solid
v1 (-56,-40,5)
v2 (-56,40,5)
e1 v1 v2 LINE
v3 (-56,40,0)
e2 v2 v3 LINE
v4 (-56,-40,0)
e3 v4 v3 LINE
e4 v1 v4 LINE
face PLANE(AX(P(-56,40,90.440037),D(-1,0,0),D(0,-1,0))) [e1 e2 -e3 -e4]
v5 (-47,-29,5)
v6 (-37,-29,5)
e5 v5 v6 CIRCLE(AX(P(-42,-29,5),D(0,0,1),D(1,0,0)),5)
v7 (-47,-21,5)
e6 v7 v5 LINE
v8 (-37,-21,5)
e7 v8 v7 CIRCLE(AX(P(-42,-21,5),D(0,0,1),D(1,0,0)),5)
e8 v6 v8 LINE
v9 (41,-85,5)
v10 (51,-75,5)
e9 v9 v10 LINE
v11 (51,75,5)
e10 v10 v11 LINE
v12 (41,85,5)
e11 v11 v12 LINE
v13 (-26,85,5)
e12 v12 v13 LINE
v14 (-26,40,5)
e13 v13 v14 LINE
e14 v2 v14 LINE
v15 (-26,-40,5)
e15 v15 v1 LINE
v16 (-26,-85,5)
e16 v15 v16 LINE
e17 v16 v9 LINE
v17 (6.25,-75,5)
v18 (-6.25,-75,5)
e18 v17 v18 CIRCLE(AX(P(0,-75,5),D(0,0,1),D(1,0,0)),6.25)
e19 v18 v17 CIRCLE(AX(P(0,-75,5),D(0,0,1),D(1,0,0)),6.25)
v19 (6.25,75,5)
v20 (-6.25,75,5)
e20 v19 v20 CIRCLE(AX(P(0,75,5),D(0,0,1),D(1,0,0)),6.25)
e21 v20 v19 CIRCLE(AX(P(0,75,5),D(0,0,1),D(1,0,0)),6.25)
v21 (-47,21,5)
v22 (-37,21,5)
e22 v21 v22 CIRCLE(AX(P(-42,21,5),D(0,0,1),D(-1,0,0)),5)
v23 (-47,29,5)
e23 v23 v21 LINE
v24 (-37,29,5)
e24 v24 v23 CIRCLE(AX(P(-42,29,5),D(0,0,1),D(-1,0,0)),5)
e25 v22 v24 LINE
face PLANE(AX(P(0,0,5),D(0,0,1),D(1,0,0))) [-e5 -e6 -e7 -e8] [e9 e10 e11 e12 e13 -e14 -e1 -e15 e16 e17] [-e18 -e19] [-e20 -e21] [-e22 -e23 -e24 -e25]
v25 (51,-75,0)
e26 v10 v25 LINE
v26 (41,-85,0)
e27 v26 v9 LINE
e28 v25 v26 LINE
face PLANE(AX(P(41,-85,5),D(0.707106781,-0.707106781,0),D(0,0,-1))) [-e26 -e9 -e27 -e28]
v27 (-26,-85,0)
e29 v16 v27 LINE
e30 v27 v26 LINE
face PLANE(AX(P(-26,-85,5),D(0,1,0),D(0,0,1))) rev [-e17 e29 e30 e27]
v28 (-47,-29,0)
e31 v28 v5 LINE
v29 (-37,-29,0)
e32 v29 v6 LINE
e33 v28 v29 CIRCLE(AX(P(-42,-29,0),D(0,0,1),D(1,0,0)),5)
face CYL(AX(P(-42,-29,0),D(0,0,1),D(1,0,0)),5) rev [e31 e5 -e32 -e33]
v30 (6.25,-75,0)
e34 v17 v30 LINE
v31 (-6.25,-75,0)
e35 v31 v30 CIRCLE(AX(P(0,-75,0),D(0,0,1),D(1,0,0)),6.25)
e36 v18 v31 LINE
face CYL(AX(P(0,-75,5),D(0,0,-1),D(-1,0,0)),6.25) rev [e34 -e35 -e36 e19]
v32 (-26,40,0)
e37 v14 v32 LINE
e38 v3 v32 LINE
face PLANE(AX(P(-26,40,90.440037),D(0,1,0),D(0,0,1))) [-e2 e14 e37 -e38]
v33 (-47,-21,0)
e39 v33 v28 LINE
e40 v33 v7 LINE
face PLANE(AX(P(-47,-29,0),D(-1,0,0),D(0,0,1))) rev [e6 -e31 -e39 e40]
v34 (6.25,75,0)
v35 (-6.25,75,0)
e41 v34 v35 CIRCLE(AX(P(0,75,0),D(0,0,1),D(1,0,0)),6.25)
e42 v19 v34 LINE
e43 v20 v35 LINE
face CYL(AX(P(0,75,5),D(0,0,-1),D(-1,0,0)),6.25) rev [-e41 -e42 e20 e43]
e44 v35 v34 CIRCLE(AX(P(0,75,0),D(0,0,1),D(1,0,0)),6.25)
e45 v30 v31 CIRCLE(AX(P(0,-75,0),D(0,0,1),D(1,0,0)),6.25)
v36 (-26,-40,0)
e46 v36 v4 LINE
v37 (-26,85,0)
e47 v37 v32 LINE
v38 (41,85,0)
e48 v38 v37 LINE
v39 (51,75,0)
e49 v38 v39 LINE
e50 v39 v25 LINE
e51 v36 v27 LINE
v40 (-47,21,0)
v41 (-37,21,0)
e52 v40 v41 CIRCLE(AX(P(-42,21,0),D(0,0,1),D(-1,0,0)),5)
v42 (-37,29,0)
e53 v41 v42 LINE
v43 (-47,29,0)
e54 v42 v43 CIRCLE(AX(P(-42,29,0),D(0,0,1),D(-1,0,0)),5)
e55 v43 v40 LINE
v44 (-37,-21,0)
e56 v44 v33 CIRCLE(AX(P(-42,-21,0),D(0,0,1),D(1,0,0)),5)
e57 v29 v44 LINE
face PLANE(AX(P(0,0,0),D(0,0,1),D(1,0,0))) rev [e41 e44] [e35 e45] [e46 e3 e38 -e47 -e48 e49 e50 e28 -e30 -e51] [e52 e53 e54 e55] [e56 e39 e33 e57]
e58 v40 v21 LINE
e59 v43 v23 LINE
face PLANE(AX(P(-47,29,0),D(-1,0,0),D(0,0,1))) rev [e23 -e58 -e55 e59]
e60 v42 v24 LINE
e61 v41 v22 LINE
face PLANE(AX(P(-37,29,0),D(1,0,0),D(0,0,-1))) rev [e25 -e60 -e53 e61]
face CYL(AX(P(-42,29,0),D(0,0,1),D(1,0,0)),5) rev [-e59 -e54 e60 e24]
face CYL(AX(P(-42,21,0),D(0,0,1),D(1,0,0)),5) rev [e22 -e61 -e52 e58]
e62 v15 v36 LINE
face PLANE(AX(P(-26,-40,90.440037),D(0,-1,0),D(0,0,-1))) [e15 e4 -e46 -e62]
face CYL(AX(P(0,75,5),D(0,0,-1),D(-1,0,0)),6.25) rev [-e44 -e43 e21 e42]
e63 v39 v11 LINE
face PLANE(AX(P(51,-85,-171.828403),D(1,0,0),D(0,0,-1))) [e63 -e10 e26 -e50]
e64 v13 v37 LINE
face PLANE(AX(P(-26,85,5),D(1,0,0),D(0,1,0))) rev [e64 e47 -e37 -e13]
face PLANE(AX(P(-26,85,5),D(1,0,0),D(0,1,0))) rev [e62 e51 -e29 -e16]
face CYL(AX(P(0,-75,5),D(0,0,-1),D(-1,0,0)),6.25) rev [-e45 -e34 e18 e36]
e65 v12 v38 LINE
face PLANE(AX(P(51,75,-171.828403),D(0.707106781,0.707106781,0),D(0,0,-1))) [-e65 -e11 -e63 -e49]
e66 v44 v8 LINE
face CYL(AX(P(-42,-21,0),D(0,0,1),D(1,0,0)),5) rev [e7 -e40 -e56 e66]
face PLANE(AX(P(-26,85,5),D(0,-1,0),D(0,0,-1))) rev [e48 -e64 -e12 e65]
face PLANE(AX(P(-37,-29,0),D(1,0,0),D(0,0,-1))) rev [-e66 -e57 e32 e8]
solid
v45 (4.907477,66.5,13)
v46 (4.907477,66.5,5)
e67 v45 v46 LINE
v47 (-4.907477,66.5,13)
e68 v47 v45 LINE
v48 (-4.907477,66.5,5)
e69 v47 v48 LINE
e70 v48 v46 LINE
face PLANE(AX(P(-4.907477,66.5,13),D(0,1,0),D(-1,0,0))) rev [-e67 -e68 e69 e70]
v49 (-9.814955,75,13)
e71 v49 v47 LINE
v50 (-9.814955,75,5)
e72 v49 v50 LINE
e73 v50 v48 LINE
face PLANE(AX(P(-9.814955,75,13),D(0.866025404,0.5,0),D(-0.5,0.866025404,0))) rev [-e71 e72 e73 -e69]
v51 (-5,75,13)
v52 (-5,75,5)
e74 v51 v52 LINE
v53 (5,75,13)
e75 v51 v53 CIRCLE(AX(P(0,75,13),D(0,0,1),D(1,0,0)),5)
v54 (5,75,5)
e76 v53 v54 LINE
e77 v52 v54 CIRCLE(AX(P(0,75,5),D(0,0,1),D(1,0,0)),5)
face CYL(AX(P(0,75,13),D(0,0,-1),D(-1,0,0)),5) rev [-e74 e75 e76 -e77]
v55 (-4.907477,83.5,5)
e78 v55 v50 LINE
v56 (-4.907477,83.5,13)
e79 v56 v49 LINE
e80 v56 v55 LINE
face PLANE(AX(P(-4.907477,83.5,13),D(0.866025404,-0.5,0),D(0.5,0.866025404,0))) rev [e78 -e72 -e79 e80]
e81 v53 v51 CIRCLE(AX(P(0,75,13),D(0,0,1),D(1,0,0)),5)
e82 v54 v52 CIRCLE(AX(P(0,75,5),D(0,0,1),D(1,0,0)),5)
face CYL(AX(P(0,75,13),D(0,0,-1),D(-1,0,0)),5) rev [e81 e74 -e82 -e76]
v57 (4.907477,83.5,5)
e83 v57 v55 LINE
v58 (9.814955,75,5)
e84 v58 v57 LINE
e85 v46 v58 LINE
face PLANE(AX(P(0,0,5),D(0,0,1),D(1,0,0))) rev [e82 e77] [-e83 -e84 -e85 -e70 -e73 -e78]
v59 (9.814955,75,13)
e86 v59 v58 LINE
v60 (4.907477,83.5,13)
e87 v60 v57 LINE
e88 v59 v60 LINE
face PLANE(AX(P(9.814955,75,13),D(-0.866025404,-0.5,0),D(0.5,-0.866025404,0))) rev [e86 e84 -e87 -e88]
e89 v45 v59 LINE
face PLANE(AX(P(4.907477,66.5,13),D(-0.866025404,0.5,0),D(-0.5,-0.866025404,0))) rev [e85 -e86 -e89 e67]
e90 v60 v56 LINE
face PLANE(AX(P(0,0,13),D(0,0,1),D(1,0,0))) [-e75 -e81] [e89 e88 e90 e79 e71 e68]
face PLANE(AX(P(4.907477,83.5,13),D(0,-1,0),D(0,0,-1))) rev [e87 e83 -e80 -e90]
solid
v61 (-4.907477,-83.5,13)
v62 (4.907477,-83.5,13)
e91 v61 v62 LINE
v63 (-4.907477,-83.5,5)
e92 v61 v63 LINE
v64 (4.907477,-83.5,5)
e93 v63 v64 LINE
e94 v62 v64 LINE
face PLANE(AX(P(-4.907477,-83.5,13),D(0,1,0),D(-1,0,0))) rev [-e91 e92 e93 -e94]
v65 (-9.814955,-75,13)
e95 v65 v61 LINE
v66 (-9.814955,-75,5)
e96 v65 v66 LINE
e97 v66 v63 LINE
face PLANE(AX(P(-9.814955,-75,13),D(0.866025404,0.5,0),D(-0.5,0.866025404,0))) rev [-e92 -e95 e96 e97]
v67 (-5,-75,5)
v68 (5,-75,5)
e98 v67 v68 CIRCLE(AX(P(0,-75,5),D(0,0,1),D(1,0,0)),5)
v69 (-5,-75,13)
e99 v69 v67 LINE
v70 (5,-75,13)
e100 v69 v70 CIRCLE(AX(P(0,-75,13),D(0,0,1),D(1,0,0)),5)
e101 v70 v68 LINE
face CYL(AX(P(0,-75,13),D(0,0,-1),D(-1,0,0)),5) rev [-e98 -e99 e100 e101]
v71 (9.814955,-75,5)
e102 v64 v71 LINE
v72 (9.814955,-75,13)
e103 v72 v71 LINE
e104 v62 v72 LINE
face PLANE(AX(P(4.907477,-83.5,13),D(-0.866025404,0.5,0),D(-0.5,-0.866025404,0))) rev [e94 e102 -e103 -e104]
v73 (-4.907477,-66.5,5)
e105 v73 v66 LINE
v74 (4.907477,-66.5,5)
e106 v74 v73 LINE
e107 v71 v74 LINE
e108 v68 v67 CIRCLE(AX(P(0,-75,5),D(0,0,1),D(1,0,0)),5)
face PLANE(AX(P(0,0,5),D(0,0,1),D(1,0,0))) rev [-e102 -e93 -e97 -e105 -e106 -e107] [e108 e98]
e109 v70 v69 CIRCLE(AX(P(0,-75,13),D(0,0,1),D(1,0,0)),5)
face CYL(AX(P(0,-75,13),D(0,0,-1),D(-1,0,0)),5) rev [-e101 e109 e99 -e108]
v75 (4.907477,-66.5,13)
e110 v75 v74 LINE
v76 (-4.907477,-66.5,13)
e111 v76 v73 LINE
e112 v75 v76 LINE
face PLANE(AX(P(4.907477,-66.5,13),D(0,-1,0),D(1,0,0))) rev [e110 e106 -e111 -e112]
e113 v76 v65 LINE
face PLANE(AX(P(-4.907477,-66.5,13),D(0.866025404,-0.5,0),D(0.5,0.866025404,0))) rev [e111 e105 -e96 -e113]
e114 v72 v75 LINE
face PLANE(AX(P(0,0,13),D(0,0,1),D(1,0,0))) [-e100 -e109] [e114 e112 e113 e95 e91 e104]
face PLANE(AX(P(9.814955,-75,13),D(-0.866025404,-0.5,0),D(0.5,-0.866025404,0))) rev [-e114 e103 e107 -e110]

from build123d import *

# Parameters (mm, degrees)
SKETCH_1_W            = 52
SKETCH_1_H            = 170
SKETCH_1_R            = 6.25
EXTRUDE_392_DEPTH     = 5
SKETCH_6_W            = 30
SKETCH_6_H            = 80
EXTRUDE_644_DEPTH     = 5
CUT_EXTRUDE_947_DEPTH = 102.911726509
SKETCH_3_R            = 5
EXTRUDE_2_DEPTH       = 8
EXTRUDE_2_2_DEPTH     = 8
SKETCH_11_W           = 25
SKETCH_11_H           = 170
EXTRUDE_3_DEPTH       = 5
CHAMFER_6_SIZE        = 10


with BuildPart() as part:
    # 草图1 → Extrude 392 (new body)
    with BuildSketch(Plane.XY):
        Rectangle(SKETCH_1_W, SKETCH_1_H)
        with Locations((0, 75)):
            Circle(SKETCH_1_R, mode=Mode.SUBTRACT)
        with Locations((0, -75)):
            Circle(SKETCH_1_R, mode=Mode.SUBTRACT)
    extrude(amount=EXTRUDE_392_DEPTH)

    # 草图6 → Extrude 644 (add)
    with BuildSketch(Plane(origin=(0, 0, 0), x_dir=(-1, 0, 0), z_dir=(0, 0, -1))):
        with Locations((41, 0)):
            Rectangle(SKETCH_6_W, SKETCH_6_H)
    extrude(amount=-EXTRUDE_644_DEPTH)

    # 草图10 → Cut-Extrude 947 (cut, through all)
    with BuildSketch(Plane.XY.offset(5)):
        with BuildLine():
            Line((-47, -29), (-47, -21))
            ThreePointArc((-47, -21), (-42, -16), (-37, -21))
            Line((-37, -21), (-37, -29))
            ThreePointArc((-37, -29), (-42, -34), (-47, -29))
        make_face()
        with BuildLine():
            Line((-47, 29), (-47, 21))
            ThreePointArc((-47, 21), (-42, 16), (-37, 21))
            Line((-37, 21), (-37, 29))
            ThreePointArc((-37, 29), (-42, 34), (-47, 29))
        make_face()
    extrude(amount=-CUT_EXTRUDE_947_DEPTH, mode=Mode.SUBTRACT)


with BuildPart() as body_2:
    # 草图3 → 凸台-拉伸2 (new body)
    with BuildSketch(Plane.XY.offset(5)):
        Polygon((9.814954576, 75), (4.907477288, 83.5), (-4.907477288, 83.5), (-9.814954576, 75), (-4.907477288, 66.5), (4.907477288, 66.5), align=None)
        with Locations((0, 75)):
            Circle(SKETCH_3_R, mode=Mode.SUBTRACT)
    extrude(amount=EXTRUDE_2_DEPTH)


with BuildPart() as body_3:
    # 草图3 → Extrude 2 2 (new body)
    with BuildSketch(Plane.XY.offset(5)):
        Polygon((9.814954576, -75), (4.907477288, -66.5), (-4.907477288, -66.5), (-9.814954576, -75), (-4.907477288, -83.5), (4.907477288, -83.5), align=None)
        with Locations((0, -75)):
            Circle(SKETCH_3_R, mode=Mode.SUBTRACT)
    extrude(amount=EXTRUDE_2_2_DEPTH)


with BuildPart() as body_4:
    # 草图11 → 凸台-拉伸3 (new body)
    with BuildSketch(Plane.XY.offset(5)):
        with Locations((38.5, 0)):
            Rectangle(SKETCH_11_W, SKETCH_11_H)
    extrude(amount=-EXTRUDE_3_DEPTH)


with BuildPart() as part_1:
    add(part.part)

    # Combine 1: union body 4
    add(body_4.part)

    # 倒角6
    chamfer_6_edges = [part_1.edges().sort_by_distance(p)[0] for p in [
        (51, 85, 2.5),
        (51, -85, 2.5),
    ]]
    chamfer(chamfer_6_edges, length=CHAMFER_6_SIZE)


solid = Compound([body_2.part, body_3.part, part_1.part])
